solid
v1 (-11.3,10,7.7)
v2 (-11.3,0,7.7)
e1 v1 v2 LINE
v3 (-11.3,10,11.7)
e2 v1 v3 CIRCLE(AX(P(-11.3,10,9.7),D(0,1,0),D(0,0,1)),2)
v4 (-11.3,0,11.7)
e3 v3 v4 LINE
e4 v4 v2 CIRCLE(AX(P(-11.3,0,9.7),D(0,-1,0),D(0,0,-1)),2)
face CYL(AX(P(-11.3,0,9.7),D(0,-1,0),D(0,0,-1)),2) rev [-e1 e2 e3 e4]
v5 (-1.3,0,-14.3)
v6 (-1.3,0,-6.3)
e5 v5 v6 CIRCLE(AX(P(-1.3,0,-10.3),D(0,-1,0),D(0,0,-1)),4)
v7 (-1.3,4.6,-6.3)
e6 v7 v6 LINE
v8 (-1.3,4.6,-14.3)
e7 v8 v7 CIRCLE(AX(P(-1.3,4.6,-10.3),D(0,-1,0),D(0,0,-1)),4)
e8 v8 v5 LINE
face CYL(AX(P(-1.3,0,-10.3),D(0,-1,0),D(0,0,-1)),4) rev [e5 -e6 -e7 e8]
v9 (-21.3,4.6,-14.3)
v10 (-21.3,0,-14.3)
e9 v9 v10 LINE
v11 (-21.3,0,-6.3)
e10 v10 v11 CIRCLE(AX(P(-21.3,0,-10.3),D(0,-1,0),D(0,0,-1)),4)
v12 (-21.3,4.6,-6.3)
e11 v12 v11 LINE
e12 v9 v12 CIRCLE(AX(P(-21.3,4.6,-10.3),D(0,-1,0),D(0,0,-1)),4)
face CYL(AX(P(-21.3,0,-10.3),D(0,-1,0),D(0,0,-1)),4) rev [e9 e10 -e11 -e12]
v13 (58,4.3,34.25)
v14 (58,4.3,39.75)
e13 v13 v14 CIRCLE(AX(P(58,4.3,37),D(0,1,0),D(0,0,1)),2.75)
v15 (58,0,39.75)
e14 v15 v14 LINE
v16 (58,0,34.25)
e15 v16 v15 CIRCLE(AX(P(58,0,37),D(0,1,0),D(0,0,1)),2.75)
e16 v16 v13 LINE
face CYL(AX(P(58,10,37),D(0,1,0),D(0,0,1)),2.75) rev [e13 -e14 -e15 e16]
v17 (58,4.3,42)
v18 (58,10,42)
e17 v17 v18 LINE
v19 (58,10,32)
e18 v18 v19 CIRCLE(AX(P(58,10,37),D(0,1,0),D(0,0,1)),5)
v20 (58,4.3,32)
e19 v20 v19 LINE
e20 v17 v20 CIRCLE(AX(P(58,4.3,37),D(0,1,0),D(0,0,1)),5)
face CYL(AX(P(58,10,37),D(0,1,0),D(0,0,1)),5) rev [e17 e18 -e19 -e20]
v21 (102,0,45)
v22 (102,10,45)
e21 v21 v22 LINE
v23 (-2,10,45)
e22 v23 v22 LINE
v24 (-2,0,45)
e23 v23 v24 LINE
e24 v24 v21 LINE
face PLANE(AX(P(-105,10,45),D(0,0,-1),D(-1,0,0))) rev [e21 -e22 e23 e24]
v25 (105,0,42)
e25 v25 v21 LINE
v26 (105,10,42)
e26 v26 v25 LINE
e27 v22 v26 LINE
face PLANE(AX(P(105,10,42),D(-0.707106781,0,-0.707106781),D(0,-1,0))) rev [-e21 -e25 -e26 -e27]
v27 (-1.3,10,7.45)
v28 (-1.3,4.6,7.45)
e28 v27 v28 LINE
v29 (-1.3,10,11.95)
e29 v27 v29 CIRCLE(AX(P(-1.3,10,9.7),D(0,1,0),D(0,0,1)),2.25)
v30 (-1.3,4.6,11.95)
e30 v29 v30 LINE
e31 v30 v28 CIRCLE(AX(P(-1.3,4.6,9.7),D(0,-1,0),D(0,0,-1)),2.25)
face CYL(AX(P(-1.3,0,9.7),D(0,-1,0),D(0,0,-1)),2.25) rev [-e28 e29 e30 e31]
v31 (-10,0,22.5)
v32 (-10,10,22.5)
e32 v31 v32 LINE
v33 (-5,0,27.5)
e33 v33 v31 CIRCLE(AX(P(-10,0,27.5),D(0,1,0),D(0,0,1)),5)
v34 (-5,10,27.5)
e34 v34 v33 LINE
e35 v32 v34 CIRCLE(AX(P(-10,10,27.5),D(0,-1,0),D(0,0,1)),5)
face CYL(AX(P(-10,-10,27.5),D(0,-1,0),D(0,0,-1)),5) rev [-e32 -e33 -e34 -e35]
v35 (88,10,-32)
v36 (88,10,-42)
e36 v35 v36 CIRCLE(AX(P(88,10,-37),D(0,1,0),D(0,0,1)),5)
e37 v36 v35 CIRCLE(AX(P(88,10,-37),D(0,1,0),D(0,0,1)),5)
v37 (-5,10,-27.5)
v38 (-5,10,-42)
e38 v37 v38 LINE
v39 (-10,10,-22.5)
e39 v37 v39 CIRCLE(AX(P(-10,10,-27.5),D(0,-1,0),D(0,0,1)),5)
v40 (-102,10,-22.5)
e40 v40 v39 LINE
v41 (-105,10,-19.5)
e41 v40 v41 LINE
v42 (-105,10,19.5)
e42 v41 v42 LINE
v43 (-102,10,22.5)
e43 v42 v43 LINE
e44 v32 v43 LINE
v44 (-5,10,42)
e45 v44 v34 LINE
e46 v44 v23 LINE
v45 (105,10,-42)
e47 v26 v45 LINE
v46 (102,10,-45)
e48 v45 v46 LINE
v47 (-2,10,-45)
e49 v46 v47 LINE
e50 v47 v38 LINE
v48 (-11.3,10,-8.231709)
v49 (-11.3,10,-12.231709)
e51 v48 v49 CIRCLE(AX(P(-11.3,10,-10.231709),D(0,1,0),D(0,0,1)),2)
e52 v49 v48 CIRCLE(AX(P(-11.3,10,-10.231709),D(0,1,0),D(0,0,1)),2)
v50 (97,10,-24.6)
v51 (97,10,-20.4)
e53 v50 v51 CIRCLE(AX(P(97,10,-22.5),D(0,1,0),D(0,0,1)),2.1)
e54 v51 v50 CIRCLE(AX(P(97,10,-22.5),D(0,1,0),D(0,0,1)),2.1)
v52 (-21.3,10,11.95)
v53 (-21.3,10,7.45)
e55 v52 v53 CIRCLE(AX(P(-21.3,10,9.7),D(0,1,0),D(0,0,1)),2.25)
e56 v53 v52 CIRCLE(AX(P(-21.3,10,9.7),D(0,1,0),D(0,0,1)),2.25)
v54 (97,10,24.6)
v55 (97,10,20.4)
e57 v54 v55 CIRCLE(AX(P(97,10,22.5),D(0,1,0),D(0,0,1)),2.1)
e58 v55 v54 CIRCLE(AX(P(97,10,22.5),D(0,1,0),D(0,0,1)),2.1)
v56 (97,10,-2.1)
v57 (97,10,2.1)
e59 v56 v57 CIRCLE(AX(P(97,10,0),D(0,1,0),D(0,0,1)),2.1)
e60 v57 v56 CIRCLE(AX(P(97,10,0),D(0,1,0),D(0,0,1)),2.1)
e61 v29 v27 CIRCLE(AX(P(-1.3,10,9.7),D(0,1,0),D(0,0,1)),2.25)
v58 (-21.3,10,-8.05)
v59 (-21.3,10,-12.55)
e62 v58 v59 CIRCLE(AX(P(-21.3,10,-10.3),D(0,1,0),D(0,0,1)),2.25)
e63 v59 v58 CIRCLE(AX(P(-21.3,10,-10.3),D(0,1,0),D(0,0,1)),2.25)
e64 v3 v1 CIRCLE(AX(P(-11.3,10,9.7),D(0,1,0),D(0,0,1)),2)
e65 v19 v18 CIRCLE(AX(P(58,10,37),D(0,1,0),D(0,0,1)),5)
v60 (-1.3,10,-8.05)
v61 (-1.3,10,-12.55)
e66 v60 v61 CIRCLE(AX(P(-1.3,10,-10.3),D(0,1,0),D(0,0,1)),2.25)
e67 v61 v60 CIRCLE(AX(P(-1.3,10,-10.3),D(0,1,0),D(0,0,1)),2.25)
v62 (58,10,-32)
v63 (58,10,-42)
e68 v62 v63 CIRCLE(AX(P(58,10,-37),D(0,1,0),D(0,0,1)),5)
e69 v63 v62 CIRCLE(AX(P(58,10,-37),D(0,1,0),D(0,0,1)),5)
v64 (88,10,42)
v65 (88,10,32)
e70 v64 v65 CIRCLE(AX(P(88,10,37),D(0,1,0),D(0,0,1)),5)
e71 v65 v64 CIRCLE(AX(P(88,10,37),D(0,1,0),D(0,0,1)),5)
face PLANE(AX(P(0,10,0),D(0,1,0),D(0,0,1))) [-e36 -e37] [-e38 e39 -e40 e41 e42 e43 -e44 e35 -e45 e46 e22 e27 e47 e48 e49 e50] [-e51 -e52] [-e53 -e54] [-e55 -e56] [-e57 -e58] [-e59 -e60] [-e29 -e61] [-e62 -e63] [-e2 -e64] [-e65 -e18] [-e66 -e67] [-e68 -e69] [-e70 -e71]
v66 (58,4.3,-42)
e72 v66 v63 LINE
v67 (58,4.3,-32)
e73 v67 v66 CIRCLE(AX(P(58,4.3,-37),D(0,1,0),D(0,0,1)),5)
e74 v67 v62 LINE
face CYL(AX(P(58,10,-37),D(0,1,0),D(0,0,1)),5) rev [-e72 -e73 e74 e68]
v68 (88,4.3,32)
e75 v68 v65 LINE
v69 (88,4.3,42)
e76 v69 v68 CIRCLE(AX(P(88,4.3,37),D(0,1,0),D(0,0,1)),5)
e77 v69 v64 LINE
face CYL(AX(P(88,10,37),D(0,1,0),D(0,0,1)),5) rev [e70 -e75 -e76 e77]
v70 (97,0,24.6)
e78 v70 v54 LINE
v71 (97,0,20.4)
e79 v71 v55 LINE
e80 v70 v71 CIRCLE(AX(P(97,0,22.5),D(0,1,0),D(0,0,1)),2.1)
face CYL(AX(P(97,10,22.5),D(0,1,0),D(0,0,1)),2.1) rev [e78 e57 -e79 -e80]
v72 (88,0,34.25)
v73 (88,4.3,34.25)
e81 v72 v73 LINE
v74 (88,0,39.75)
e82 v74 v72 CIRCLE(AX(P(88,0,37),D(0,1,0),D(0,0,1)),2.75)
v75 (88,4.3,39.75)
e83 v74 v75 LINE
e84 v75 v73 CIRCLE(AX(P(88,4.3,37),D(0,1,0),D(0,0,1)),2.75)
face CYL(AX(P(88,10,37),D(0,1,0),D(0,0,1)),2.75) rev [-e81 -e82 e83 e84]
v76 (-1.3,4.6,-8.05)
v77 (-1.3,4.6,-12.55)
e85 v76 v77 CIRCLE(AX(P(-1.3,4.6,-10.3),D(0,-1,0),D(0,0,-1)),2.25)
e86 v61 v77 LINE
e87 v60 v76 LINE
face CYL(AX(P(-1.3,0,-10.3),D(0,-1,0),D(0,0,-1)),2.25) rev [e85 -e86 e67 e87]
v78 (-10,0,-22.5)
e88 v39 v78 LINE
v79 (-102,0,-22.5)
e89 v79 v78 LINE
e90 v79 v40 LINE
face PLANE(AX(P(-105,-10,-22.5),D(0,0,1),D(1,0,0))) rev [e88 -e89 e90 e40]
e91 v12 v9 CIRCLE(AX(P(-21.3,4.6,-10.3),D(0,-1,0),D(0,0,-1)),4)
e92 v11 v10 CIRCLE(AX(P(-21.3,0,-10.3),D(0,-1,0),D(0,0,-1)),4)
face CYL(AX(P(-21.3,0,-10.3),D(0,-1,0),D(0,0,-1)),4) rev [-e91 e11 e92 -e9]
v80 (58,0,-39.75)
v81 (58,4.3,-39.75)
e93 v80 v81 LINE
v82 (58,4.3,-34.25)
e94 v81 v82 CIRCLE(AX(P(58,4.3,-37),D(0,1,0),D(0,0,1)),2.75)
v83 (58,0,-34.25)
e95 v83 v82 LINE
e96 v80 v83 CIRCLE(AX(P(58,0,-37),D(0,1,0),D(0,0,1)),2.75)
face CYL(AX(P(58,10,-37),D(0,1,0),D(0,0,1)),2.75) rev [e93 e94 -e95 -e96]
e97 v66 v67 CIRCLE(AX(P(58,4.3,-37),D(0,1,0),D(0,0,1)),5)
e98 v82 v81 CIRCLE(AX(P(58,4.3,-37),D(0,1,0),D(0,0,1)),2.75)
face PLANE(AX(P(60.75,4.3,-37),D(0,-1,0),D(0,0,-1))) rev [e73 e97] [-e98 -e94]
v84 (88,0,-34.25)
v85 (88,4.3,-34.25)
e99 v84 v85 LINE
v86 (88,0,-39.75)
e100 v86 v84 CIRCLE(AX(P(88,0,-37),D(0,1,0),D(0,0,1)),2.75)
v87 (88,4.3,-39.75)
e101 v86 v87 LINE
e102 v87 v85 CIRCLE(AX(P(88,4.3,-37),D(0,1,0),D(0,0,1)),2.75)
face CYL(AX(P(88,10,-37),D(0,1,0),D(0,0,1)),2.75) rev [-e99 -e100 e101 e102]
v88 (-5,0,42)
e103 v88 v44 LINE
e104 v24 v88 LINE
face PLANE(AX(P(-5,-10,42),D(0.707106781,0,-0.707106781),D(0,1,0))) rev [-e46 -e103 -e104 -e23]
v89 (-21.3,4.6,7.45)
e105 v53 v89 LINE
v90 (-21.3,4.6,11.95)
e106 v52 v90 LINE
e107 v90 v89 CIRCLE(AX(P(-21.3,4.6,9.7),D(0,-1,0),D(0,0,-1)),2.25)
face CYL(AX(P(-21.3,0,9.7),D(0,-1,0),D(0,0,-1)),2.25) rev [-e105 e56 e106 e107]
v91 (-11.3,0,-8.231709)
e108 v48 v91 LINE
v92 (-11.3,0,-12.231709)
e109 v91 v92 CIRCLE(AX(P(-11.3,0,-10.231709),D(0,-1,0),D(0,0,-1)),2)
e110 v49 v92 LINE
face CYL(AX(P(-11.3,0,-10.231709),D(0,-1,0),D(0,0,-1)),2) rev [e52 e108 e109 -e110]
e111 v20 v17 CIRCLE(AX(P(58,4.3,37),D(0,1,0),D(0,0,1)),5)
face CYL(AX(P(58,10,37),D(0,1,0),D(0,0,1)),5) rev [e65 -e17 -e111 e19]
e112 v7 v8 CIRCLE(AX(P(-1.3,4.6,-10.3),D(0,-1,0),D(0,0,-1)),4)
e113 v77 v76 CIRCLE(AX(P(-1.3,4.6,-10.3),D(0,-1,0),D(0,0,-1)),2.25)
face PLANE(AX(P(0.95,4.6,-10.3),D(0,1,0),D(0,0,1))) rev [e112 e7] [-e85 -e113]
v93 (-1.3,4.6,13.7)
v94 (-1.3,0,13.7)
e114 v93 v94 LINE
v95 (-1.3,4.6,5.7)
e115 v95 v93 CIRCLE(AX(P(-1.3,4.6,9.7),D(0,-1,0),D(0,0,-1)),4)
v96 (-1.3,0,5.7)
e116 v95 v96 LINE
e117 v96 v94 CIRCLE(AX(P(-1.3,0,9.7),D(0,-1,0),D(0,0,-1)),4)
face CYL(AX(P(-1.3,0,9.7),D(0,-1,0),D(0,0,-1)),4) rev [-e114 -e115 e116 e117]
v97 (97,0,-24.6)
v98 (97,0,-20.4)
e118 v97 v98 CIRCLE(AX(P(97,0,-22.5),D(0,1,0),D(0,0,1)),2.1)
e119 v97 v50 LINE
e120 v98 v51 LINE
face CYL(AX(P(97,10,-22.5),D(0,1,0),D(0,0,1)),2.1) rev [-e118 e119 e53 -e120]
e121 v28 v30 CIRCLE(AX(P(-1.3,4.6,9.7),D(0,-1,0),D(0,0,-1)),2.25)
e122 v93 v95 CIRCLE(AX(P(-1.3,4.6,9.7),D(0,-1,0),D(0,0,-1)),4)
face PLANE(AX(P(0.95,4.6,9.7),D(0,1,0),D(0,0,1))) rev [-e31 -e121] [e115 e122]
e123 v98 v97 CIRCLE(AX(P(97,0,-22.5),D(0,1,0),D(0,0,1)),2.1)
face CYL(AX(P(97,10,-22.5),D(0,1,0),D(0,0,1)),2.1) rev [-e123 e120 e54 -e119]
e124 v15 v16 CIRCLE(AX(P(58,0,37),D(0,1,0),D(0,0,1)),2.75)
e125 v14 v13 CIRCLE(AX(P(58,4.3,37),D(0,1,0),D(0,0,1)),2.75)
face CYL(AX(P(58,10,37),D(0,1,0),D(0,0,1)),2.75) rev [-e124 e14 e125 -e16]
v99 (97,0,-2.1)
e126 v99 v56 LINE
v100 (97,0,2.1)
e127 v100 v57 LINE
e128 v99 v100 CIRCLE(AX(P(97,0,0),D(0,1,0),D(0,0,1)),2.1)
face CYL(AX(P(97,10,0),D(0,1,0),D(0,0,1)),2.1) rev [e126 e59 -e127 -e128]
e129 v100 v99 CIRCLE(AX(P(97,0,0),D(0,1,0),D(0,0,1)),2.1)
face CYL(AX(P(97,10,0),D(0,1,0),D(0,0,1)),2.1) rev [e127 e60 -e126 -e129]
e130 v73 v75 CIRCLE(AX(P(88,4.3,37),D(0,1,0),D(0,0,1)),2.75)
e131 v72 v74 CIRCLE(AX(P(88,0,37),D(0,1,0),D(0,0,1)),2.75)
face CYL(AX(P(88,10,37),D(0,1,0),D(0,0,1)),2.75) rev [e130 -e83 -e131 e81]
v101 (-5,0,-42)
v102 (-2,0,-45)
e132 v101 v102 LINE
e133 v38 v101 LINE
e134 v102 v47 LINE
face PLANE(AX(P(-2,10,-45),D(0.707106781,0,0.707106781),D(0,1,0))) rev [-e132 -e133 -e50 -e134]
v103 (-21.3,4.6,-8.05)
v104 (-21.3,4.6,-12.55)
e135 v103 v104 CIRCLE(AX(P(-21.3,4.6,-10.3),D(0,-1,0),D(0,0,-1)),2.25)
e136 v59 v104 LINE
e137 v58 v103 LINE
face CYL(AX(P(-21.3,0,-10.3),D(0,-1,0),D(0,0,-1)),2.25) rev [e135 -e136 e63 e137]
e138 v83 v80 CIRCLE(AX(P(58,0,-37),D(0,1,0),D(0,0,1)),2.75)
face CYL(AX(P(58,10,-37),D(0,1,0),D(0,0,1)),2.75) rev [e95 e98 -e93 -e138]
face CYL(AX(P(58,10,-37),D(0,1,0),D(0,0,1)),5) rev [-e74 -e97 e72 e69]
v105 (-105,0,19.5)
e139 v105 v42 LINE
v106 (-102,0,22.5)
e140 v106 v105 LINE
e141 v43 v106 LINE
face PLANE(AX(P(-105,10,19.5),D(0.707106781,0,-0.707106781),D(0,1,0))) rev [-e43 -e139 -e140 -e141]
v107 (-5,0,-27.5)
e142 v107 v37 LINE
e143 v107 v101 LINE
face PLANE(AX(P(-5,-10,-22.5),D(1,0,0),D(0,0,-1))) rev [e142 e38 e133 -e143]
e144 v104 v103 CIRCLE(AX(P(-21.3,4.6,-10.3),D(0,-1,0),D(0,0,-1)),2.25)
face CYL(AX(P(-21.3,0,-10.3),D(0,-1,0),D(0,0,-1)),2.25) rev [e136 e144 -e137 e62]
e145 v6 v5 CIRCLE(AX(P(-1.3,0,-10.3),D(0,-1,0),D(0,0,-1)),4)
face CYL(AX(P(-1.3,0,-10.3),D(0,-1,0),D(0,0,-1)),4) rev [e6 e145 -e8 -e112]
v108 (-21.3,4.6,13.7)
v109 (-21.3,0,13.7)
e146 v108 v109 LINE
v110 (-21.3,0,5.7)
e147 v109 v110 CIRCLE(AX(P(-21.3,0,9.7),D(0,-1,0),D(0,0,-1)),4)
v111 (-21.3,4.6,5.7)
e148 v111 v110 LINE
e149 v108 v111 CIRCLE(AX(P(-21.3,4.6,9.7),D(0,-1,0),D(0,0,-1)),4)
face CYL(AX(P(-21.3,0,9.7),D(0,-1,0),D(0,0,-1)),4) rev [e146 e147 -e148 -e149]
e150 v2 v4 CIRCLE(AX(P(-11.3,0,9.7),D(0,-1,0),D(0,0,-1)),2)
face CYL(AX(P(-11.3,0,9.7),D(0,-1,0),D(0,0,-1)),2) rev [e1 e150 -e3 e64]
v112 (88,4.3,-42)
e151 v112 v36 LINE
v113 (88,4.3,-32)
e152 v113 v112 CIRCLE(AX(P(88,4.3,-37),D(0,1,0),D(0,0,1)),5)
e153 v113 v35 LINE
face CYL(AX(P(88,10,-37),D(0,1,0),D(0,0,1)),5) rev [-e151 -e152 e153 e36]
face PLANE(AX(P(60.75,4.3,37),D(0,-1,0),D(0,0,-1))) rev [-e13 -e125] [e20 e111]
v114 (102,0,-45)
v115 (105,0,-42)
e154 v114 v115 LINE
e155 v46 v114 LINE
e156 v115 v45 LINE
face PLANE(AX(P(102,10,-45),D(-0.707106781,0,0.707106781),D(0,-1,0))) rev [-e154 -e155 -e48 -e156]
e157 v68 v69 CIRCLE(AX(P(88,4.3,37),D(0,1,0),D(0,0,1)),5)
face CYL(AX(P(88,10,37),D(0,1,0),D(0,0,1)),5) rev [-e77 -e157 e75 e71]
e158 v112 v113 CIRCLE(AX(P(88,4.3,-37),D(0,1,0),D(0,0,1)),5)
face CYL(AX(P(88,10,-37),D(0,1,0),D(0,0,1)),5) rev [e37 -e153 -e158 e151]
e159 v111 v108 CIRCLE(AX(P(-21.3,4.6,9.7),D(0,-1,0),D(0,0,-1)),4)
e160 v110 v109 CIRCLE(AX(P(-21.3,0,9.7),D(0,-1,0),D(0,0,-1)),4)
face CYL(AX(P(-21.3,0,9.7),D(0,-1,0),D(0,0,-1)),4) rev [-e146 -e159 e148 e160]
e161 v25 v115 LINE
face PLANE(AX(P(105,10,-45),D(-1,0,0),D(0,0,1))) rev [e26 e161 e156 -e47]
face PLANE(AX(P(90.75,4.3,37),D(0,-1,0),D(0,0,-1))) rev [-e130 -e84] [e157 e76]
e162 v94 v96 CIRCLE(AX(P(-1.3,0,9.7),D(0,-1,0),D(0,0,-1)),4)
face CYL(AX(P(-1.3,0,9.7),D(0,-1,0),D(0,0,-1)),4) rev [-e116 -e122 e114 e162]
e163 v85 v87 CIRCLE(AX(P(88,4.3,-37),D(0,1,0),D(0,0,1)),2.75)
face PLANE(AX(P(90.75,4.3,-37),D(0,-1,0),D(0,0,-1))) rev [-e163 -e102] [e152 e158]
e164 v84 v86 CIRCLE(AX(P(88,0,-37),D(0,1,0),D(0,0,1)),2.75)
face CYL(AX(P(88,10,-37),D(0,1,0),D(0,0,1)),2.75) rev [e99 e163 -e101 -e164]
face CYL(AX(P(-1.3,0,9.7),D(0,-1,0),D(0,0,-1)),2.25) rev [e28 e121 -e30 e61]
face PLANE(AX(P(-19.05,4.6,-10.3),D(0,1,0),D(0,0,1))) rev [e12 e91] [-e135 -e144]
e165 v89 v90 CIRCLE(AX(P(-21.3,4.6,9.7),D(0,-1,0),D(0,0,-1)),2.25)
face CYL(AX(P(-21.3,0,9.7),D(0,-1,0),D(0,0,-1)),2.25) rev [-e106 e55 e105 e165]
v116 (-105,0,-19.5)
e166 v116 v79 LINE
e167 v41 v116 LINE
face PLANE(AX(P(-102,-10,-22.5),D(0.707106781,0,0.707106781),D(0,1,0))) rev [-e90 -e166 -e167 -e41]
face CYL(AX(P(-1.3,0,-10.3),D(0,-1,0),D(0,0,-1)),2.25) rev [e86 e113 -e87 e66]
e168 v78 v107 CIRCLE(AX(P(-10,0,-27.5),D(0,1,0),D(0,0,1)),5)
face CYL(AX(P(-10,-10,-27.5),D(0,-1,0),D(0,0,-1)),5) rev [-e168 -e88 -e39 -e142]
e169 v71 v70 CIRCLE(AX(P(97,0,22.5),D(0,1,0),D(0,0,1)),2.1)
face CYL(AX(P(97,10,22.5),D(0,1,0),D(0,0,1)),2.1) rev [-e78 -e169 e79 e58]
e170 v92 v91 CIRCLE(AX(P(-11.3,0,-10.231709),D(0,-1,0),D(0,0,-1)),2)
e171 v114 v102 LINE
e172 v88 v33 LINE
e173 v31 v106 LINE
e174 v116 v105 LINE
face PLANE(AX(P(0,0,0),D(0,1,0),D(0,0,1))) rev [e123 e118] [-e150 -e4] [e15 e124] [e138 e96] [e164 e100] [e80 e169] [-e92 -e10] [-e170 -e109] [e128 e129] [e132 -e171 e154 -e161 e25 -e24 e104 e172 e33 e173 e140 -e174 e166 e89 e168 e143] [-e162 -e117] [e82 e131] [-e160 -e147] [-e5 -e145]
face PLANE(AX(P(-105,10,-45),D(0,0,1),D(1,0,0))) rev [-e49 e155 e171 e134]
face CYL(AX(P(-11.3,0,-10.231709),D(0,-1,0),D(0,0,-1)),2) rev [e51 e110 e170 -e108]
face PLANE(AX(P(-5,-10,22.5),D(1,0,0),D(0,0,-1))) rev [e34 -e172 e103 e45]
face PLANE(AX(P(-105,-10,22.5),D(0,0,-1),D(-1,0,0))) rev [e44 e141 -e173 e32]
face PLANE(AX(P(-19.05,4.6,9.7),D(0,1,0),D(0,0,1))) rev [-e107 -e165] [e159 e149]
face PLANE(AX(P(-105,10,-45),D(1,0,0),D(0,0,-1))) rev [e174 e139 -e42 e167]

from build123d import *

# Parameters (mm, degrees)
SKETCH_1_W                = 210
SKETCH_1_H                = 90
EXTRUDE_1_DEPTH           = 10
CHAMFER_1_SIZE            = 3
HOLE_WIZARD_2_D           = 5.5
HOLE_WIZARD_2_DEPTH       = 10.1
HOLE_WIZARD_2_CBORE_D     = 10
HOLE_WIZARD_2_CBORE_DEPTH = 5.7
HOLE_WIZARD_2_TIP         = 1.652366702
SKETCH_4_W                = 100
SKETCH_4_H                = 22.5
CUT_EXTRUDE_1_DEPTH       = 20
CHAMFER_2_SIZE            = 3
FILLET_1_R                = 5
HOLE_WIZARD_0_D           = 4.5
HOLE_WIZARD_0_DEPTH       = 25
HOLE_WIZARD_0_CBORE_D     = 8
HOLE_WIZARD_0_CBORE_DEPTH = 4.6
HOLE_WIZARD_0_TIP         = 1.351936393
MM_0_D                    = 4
MM_0_DEPTH                = 25
MM_0_TIP                  = 1.201721238
HOLE_WIZARD_M5_1_D        = 4.2
HOLE_WIZARD_M5_1_DEPTH    = 12.4
HOLE_WIZARD_M5_1_TIP      = 1.2618073


with BuildPart() as part:
    # 草图1 → 凸台-拉伸1 (new body)
    with BuildSketch(Plane(origin=(0, 0, 0), x_dir=(1, 0, 0), z_dir=(0, 1, 0))):
        Rectangle(SKETCH_1_W, SKETCH_1_H)
    extrude(amount=EXTRUDE_1_DEPTH)

    # 倒角1
    chamfer_1_edges = [part.edges().sort_by_distance(p)[0] for p in [
        (105, 5, 45),
        (-105, 5, 45),
        (-105, 5, -45),
        (105, 5, -45),
    ]]
    chamfer(chamfer_1_edges, length=CHAMFER_1_SIZE)

    # 打孔尺寸(%根据)内六角圆柱头螺钉的类型2
    with Locations(Plane(origin=(0, 10, 0), x_dir=(1, 0, 0), z_dir=(0, 1, 0))):
        with Locations((58, -37), (58, 37), (88, 37), (88, -37)):
            CounterBoreHole(HOLE_WIZARD_2_D / 2, HOLE_WIZARD_2_CBORE_D / 2, HOLE_WIZARD_2_CBORE_DEPTH, depth=HOLE_WIZARD_2_DEPTH)
            with Locations((0, 0, -(HOLE_WIZARD_2_DEPTH + HOLE_WIZARD_2_TIP / 2))):  # 118° drill point
                Cone(0, HOLE_WIZARD_2_D / 2, HOLE_WIZARD_2_TIP, mode=Mode.SUBTRACT)

    # 草图4 → 切除-拉伸1 (cut)
    with BuildSketch(Plane(origin=(0, 10, 0), x_dir=(1, 0, 0), z_dir=(0, 1, 0))):
        with Locations((-55, -33.75)):
            Rectangle(SKETCH_4_W, SKETCH_4_H)
        with Locations((-55, 33.75)):
            Rectangle(SKETCH_4_W, SKETCH_4_H)
    extrude(amount=-CUT_EXTRUDE_1_DEPTH, mode=Mode.SUBTRACT)

    # 倒角2
    chamfer_2_edges = [part.edges().sort_by_distance(p)[0] for p in [
        (-105, 5, 22.5),
        (-5, 5, 45),
        (-5, 5, -45),
        (-105, 5, -22.5),
    ]]
    chamfer(chamfer_2_edges, length=CHAMFER_2_SIZE)

    # 圆角1
    fillet_1_edges = [part.edges().sort_by_distance(p)[0] for p in [
        (-5, 5, 22.5),
        (-5, 5, -22.5),
    ]]
    fillet(fillet_1_edges, radius=FILLET_1_R)

    # 打孔尺寸(%根据)内六角圆柱头螺钉的类型0
    with Locations(Plane(origin=(0, 0, 0), x_dir=(-1, 0, 0), z_dir=(0, -1, 0))):
        with Locations((21.3, 10.3), (21.3, -9.7), (1.3, 10.3), (1.3, -9.7)):
            CounterBoreHole(HOLE_WIZARD_0_D / 2, HOLE_WIZARD_0_CBORE_D / 2, HOLE_WIZARD_0_CBORE_DEPTH, depth=HOLE_WIZARD_0_DEPTH)
            with Locations((0, 0, -(HOLE_WIZARD_0_DEPTH + HOLE_WIZARD_0_TIP / 2))):  # 118° drill point
                Cone(0, HOLE_WIZARD_0_D / 2, HOLE_WIZARD_0_TIP, mode=Mode.SUBTRACT)

    # 大小mm 暗销孔0
    with Locations(Plane(origin=(0, 0, 0), x_dir=(-1, 0, 0), z_dir=(0, -1, 0))):
        with Locations((11.3, -9.7), (11.3, 10.231708661)):
            Hole(MM_0_D / 2, depth=MM_0_DEPTH)
            with Locations((0, 0, -(MM_0_DEPTH + MM_0_TIP / 2))):  # 118° drill point
                Cone(0, MM_0_D / 2, MM_0_TIP, mode=Mode.SUBTRACT)

    # M5 螺纹孔1
    with Locations(Plane(origin=(0, 10, 0), x_dir=(1, 0, 0), z_dir=(0, 1, 0))):
        with Locations((97, -22.5), (97, 0), (97, 22.5)):
            Hole(HOLE_WIZARD_M5_1_D / 2, depth=HOLE_WIZARD_M5_1_DEPTH)
            with Locations((0, 0, -(HOLE_WIZARD_M5_1_DEPTH + HOLE_WIZARD_M5_1_TIP / 2))):  # 118° drill point
                Cone(0, HOLE_WIZARD_M5_1_D / 2, HOLE_WIZARD_M5_1_TIP, mode=Mode.SUBTRACT)


solid = part.part
